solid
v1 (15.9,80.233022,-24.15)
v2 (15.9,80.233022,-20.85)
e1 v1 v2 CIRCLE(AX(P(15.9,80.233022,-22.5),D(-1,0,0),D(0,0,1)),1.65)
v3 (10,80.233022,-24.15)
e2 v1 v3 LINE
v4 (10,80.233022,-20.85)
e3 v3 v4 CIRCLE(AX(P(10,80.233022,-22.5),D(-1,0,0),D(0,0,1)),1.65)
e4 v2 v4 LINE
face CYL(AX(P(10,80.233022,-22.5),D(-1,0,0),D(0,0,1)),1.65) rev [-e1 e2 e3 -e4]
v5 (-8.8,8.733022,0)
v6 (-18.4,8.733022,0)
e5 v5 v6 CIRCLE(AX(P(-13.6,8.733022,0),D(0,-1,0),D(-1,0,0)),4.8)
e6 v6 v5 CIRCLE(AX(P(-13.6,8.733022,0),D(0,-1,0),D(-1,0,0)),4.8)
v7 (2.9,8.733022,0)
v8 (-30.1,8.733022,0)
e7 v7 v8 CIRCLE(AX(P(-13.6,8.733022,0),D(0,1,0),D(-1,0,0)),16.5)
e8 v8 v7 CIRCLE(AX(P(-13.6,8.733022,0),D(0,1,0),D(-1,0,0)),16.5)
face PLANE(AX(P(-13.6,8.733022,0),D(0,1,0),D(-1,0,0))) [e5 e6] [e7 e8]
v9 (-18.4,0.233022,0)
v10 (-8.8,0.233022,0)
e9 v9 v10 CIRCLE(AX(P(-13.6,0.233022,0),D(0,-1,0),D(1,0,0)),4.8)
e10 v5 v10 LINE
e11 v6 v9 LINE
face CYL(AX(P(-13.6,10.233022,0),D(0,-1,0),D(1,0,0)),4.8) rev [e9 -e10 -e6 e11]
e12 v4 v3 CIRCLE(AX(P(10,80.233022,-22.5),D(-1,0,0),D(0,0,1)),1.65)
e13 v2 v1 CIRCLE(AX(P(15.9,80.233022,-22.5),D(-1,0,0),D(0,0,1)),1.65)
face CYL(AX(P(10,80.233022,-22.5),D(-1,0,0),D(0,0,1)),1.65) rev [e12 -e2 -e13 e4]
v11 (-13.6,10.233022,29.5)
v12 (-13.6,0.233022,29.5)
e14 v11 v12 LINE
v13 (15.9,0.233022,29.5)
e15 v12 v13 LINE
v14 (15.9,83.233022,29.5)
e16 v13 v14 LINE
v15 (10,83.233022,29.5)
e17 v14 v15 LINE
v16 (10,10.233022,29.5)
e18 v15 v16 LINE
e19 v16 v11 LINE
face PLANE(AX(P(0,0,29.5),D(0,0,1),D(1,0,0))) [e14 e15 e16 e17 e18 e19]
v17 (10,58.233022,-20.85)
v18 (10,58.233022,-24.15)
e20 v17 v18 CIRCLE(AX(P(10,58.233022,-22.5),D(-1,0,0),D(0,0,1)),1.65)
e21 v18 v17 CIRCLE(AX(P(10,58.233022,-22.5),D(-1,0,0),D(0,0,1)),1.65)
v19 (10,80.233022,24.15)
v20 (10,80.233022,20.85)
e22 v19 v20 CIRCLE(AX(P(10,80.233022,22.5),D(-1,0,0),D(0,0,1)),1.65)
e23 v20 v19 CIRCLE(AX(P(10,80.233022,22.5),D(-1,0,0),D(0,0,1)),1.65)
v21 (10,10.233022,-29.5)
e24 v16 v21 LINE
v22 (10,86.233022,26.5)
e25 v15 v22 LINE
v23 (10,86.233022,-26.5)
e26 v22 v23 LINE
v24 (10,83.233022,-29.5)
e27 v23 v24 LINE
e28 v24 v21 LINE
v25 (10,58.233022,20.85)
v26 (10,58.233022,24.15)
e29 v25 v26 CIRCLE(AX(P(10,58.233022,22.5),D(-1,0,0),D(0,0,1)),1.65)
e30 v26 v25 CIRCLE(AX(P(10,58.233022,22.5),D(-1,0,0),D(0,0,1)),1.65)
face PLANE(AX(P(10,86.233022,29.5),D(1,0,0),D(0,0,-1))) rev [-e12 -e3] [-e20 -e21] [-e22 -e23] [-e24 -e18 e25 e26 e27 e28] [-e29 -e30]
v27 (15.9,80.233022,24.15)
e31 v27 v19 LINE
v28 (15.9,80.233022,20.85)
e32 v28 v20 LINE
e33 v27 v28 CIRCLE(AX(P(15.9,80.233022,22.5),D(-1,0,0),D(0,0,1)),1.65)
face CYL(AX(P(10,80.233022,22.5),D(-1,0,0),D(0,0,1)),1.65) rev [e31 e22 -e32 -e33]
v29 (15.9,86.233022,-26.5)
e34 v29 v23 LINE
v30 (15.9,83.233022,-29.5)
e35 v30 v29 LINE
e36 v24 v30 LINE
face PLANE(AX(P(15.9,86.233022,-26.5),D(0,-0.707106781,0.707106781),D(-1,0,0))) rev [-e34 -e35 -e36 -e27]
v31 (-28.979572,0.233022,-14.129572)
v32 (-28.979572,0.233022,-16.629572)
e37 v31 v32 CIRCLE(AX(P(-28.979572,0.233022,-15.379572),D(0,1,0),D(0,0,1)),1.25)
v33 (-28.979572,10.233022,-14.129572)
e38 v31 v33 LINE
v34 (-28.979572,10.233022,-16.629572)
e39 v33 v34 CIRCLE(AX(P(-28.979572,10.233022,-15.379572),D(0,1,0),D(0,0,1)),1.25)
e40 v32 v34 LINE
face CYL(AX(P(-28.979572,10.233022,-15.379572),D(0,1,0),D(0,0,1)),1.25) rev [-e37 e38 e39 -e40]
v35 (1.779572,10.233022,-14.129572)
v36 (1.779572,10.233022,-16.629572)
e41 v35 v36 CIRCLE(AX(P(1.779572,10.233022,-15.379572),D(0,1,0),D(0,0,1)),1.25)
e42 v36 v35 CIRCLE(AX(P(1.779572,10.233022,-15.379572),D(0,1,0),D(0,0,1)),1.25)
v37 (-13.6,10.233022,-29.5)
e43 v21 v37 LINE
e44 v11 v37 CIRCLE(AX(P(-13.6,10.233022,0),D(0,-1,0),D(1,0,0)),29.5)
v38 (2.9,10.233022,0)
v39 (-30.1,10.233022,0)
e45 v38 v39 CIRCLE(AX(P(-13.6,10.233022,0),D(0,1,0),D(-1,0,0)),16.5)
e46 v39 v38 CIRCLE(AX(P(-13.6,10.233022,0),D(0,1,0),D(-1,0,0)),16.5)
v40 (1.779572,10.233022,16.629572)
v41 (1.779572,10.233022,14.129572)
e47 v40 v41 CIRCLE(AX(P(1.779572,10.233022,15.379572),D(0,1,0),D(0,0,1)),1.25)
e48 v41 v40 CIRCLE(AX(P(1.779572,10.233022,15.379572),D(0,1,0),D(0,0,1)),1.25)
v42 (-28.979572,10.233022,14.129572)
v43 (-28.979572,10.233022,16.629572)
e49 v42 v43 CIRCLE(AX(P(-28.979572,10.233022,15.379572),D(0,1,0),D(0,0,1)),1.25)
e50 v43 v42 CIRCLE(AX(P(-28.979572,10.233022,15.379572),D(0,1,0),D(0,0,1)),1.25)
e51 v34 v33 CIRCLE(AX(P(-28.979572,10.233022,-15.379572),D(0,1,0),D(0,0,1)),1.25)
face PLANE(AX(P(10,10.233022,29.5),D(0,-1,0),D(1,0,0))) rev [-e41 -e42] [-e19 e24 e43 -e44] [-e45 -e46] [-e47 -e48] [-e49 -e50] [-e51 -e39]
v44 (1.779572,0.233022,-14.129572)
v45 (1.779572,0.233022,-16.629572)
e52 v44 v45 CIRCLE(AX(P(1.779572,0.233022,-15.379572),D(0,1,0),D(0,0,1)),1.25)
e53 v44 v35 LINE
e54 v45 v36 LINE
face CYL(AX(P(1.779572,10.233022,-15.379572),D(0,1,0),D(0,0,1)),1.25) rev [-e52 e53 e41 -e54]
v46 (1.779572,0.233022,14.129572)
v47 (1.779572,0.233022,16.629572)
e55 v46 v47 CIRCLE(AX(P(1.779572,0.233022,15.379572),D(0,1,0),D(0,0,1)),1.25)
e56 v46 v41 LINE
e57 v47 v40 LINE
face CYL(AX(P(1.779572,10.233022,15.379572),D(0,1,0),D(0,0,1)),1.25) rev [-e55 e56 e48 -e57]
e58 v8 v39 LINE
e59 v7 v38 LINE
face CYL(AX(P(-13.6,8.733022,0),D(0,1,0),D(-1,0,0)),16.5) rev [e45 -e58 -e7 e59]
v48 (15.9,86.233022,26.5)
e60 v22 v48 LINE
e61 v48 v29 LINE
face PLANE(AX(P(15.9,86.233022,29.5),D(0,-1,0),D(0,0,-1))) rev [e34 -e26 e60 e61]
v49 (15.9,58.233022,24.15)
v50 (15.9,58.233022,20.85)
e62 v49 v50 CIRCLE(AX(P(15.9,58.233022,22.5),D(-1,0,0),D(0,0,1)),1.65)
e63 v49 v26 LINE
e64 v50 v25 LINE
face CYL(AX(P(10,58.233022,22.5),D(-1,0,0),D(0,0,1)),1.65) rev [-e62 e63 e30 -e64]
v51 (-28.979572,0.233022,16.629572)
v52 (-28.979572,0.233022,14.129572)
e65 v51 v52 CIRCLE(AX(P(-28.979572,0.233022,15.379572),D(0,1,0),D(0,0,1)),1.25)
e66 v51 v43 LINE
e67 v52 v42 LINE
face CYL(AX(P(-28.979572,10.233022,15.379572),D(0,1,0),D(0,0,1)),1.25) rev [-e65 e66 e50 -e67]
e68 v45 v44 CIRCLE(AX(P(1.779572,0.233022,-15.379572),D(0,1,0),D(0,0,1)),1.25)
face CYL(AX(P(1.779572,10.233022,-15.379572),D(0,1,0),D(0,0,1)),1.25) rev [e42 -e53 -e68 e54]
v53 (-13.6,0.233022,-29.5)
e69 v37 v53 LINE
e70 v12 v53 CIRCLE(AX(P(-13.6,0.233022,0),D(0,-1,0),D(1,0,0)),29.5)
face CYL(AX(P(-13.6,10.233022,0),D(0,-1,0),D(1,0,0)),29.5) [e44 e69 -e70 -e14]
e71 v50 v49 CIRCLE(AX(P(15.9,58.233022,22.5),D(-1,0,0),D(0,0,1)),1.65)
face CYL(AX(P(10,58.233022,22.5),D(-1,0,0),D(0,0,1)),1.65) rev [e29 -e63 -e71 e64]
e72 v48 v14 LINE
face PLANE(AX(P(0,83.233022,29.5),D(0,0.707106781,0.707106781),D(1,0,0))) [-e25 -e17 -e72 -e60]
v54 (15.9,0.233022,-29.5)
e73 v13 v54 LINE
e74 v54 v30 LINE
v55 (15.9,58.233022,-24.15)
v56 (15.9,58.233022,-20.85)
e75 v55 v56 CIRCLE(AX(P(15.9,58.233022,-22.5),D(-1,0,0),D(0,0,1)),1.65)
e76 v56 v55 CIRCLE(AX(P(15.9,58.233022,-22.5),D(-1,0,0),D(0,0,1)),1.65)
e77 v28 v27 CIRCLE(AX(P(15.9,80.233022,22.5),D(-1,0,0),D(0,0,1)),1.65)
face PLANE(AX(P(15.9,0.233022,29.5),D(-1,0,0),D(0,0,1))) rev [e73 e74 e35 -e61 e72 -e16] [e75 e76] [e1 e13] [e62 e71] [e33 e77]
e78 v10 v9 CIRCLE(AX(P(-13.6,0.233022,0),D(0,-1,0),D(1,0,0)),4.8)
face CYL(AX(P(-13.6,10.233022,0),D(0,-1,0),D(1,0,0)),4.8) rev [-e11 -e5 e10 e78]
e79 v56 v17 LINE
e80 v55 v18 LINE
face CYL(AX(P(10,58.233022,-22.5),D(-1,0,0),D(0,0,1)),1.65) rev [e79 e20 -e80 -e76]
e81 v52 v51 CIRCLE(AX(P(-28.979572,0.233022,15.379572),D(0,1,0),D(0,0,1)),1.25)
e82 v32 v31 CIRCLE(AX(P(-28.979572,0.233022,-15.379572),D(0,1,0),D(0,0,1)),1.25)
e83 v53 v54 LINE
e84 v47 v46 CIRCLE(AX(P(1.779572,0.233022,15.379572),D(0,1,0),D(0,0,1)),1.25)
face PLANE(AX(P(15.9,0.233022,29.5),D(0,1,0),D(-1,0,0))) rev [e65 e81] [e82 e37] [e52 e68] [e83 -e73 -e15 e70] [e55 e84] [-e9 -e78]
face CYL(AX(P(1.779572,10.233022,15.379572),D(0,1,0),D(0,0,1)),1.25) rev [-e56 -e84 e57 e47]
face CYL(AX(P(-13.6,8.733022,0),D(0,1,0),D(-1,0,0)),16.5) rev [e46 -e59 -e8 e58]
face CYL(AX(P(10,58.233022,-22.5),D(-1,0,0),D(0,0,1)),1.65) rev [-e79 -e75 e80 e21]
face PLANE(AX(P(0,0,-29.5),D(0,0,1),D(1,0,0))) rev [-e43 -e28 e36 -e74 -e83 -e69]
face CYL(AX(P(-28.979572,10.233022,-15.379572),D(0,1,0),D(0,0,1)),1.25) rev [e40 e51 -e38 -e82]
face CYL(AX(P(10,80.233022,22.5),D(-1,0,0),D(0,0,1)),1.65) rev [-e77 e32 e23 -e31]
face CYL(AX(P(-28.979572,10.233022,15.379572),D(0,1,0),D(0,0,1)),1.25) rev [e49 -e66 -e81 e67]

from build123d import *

# Parameters (mm, degrees)
BOSS_EXTRUDE1_DEPTH = 29.5
SKETCH2_R           = 4.8
CUT_EXTRUDE1_DEPTH  = 10
SKETCH4_R           = 16.5
CUT_EXTRUDE2_DEPTH  = 1.5
M3_TAPPED_HOLE1_D   = 2.5
CHAMFER1_SIZE       = 3
M4_TAPPED_HOLE1_D   = 3.3


with BuildPart() as part:
    # Sketch1 → Boss-Extrude1 (new, symmetric)
    with BuildSketch(Plane.XY):
        Polygon((15.9, 0.233022363), (-43.1, 0.233022363), (-43.1, 10.233022363), (10, 10.233022363), (10, 86.233022363), (15.9, 86.233022363), align=None)
    extrude(amount=BOSS_EXTRUDE1_DEPTH, both=True)

    # Sketch2 → Cut-Extrude1 (cut)
    with BuildSketch(Plane.XZ.offset(-0.233022363)):
        with BuildLine():
            ThreePointArc((-43.1, 0), (-34.459650045, 20.859650045), (-13.6, 29.5))
            Line((-13.6, 29.5), (-43.1, 29.5))
            Line((-43.1, 29.5), (-43.1, 0))
        make_face()
        with BuildLine():
            ThreePointArc((-13.6, -29.5), (-34.459650045, -20.859650045), (-43.1, 0))
            Line((-43.1, 0), (-43.1, -29.5))
            Line((-43.1, -29.5), (-13.6, -29.5))
        make_face()
        with Locations((-13.6, 0)):
            Circle(SKETCH2_R)
    extrude(amount=-CUT_EXTRUDE1_DEPTH, mode=Mode.SUBTRACT)

    # Sketch4 → Cut-Extrude2 (cut)
    with BuildSketch(Plane(origin=(0, 10.233022363, 0), x_dir=(1, 0, 0), z_dir=(0, 1, 0))):
        with Locations(Location((-13.6, 0, 0), (0, 0, 180))):
            Circle(SKETCH4_R)
    extrude(amount=-CUT_EXTRUDE2_DEPTH, mode=Mode.SUBTRACT)

    # M3 Tapped Hole1 (through all)
    with Locations(Plane(origin=(0, 10.233022363, 0), x_dir=(1, 0, 0), z_dir=(0, 1, 0))):
        with Locations((-28.979572491, -15.379572491), (-28.979572491, 15.379572491), (1.779572491, 15.379572491), (1.779572491, -15.379572491)):
            Hole(M3_TAPPED_HOLE1_D / 2)

    # Chamfer1
    chamfer1_edges = [part.edges().sort_by_distance(p)[0] for p in [
        (12.95, 86.233022363, 29.5),
        (12.95, 86.233022363, -29.5),
    ]]
    chamfer(chamfer1_edges, length=CHAMFER1_SIZE)

    # M4 Tapped Hole1 (through all)
    with Locations(Plane.ZY.offset(-10)):
        with Locations((-22.5, 80.233022363), (-22.5, 58.233022363), (22.5, 58.233022363), (22.5, 80.233022363)):
            Hole(M4_TAPPED_HOLE1_D / 2)


solid = part.part
